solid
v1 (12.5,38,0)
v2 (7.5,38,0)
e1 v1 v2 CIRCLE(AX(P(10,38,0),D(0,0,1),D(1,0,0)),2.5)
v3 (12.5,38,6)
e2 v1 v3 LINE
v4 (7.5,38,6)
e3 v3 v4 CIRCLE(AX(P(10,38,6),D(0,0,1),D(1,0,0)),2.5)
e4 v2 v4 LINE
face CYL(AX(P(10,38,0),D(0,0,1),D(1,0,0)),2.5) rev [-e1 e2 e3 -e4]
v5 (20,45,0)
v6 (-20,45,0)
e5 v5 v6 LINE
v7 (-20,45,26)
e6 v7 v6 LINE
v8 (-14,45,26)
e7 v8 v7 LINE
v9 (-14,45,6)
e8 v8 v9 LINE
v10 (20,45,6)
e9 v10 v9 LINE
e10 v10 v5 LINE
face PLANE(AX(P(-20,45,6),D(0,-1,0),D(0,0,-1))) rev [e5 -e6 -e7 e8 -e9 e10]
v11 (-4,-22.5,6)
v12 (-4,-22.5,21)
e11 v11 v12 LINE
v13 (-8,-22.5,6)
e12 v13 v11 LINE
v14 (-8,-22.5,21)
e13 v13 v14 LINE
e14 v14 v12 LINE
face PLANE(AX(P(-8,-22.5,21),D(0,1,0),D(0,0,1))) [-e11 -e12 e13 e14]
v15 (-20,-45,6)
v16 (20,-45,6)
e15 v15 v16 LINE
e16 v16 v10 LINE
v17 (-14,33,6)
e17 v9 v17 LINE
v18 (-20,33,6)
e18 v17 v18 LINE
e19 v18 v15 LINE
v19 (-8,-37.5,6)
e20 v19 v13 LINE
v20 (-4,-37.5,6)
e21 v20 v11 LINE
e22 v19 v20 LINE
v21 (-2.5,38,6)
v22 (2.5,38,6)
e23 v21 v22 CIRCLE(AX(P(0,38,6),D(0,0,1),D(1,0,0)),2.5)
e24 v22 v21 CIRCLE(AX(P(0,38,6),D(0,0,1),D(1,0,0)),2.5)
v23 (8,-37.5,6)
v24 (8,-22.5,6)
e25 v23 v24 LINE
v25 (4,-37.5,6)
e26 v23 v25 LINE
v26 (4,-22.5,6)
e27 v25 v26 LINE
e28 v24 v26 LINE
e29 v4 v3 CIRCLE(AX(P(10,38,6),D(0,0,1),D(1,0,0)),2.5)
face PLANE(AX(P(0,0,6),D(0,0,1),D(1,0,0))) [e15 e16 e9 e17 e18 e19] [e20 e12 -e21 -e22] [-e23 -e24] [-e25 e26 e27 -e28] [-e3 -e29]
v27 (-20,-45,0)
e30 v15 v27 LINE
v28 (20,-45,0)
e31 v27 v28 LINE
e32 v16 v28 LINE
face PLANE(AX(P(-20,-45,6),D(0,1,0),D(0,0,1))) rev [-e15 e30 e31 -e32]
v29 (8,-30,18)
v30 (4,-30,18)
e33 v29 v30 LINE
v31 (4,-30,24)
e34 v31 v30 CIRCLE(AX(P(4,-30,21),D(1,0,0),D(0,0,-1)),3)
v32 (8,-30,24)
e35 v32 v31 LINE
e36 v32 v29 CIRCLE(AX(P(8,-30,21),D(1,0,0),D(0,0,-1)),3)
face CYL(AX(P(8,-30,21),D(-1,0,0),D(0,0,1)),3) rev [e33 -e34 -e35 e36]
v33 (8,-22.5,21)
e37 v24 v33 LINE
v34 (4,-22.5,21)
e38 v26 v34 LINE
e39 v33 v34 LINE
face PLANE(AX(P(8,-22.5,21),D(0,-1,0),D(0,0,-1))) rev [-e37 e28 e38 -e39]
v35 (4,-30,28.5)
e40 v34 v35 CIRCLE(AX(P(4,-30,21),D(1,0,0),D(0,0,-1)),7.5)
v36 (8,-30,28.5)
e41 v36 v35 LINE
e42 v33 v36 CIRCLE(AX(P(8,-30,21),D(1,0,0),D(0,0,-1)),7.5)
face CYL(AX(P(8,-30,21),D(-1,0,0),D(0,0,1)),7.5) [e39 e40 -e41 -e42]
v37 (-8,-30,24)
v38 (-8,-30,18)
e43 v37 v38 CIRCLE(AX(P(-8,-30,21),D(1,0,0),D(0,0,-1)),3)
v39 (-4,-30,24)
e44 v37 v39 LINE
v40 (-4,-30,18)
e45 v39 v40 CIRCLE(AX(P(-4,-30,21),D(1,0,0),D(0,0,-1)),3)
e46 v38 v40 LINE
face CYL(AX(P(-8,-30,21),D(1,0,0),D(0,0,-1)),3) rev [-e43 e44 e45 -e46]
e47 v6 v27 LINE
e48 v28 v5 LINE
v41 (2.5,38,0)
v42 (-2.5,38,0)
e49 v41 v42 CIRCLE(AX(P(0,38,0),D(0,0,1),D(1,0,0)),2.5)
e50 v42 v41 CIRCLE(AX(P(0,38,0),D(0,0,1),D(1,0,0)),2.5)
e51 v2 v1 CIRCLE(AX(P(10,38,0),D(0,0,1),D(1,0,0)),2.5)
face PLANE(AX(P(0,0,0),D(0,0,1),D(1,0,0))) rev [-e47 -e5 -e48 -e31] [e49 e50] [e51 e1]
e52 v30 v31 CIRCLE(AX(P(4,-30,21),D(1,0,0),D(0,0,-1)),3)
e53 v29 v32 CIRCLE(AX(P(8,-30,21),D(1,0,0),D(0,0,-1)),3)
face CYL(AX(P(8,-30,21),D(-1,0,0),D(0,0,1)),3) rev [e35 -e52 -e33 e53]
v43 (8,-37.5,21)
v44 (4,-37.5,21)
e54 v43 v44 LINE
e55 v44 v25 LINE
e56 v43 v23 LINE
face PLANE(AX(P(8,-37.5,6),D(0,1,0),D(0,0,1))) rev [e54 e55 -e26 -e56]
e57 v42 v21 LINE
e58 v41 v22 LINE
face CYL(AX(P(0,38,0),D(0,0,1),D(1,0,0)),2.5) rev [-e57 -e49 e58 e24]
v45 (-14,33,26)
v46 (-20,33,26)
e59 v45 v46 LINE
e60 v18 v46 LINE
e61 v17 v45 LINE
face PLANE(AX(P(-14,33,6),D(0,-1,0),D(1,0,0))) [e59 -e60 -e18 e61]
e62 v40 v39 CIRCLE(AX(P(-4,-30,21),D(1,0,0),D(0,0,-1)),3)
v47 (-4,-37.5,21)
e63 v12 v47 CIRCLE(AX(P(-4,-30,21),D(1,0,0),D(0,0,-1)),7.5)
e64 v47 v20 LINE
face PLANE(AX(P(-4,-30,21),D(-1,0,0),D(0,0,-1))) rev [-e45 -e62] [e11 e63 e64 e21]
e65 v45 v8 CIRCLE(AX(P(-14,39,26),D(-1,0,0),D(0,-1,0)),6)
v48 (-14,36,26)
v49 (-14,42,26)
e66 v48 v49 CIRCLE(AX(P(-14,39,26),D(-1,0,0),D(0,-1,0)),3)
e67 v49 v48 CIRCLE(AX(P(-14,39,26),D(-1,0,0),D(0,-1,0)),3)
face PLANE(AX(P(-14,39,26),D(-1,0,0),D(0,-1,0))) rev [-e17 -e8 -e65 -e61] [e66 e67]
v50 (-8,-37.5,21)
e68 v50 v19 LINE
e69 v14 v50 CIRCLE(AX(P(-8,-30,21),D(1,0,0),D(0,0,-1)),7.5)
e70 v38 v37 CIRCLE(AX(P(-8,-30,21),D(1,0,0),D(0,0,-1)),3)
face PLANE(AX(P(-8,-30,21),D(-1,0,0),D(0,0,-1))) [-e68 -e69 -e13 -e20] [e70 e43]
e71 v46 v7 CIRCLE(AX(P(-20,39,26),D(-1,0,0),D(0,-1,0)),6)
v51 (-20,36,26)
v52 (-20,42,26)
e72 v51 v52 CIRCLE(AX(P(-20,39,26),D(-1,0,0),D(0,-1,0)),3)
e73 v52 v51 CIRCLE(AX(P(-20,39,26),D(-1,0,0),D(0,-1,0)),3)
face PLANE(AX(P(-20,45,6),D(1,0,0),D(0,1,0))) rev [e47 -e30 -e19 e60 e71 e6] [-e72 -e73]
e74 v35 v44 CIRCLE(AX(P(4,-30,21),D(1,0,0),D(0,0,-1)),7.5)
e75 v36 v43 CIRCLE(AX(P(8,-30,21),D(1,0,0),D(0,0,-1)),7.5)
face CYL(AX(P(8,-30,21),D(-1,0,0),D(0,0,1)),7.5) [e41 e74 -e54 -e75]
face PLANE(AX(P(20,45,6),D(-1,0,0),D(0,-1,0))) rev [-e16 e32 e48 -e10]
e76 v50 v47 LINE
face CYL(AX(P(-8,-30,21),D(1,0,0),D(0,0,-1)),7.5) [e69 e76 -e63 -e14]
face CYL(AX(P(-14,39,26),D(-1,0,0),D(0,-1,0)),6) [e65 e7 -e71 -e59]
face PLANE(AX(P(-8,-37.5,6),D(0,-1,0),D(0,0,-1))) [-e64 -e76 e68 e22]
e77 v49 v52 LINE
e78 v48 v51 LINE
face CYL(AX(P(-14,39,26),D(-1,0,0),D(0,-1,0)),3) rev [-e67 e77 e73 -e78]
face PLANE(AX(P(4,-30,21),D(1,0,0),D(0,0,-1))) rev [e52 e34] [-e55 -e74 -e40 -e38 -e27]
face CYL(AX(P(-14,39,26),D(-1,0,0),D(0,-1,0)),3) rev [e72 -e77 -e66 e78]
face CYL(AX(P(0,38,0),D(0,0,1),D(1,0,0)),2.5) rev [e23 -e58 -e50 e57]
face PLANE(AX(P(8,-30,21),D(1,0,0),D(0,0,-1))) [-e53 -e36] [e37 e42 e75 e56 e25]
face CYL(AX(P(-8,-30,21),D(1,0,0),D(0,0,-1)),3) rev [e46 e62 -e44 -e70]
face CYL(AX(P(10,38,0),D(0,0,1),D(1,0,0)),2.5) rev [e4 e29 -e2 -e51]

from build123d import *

# Parameters (mm, degrees)
SKETCH1_W           = 40
SKETCH1_H           = 90
BOSS_EXTRUDE1_DEPTH = 6
SKETCH2_R           = 2.5
CUT_EXTRUDE1_DEPTH  = 6
SKETCH3_R           = 3
BOSS_EXTRUDE2_DEPTH = 6
BOSS_EXTRUDE3_START = 4
SKETCH4_R           = 3
BOSS_EXTRUDE3_DEPTH = 4


with BuildPart() as part:
    # Sketch1 → Boss-Extrude1 (new body)
    with BuildSketch(Plane.XY):
        Rectangle(SKETCH1_W, SKETCH1_H)
    extrude(amount=BOSS_EXTRUDE1_DEPTH)

    # Sketch2 → Cut-Extrude1 (cut)
    with BuildSketch(Plane.XY.offset(6)):
        with Locations((0, 38)):
            Circle(SKETCH2_R)
        with Locations((10, 38)):
            Circle(SKETCH2_R)
    extrude(amount=-CUT_EXTRUDE1_DEPTH, mode=Mode.SUBTRACT)

    # Sketch3 → Boss-Extrude2 (add)
    with BuildSketch(Plane.ZY.offset(20)):
        with BuildLine():
            Line((26, 45), (6, 45))
            Line((6, 45), (6, 33))
            Line((6, 33), (26, 33))
            ThreePointArc((26, 33), (32, 39), (26, 45))
        make_face()
        with Locations(Location((26, 39, 0), (0, 0, 270))):
            Circle(SKETCH3_R, mode=Mode.SUBTRACT)
    extrude(amount=-BOSS_EXTRUDE2_DEPTH)

    # Sketch4 → Boss-Extrude3 (add)
    with BuildSketch(Plane(origin=(0, 0, 0), x_dir=(0, 0, -1), z_dir=(1, 0, 0)).offset(BOSS_EXTRUDE3_START)):
        with BuildLine():
            Line((-21, -22.5), (-6, -22.5))
            Line((-6, -22.5), (-6, -37.5))
            Line((-6, -37.5), (-21, -37.5))
            ThreePointArc((-21, -37.5), (-28.5, -30), (-21, -22.5))
        make_face()
        with Locations((-21, -30)):
            Circle(SKETCH4_R, mode=Mode.SUBTRACT)
    boss_extrude3 = extrude(amount=BOSS_EXTRUDE3_DEPTH)

    # Mirror1: Boss-Extrude3 across plane
    add(boss_extrude3.mirror(Plane(origin=(0, 0, 0), x_dir=(0, 0, 1), z_dir=(1, 0, 0))))


solid = part.part
